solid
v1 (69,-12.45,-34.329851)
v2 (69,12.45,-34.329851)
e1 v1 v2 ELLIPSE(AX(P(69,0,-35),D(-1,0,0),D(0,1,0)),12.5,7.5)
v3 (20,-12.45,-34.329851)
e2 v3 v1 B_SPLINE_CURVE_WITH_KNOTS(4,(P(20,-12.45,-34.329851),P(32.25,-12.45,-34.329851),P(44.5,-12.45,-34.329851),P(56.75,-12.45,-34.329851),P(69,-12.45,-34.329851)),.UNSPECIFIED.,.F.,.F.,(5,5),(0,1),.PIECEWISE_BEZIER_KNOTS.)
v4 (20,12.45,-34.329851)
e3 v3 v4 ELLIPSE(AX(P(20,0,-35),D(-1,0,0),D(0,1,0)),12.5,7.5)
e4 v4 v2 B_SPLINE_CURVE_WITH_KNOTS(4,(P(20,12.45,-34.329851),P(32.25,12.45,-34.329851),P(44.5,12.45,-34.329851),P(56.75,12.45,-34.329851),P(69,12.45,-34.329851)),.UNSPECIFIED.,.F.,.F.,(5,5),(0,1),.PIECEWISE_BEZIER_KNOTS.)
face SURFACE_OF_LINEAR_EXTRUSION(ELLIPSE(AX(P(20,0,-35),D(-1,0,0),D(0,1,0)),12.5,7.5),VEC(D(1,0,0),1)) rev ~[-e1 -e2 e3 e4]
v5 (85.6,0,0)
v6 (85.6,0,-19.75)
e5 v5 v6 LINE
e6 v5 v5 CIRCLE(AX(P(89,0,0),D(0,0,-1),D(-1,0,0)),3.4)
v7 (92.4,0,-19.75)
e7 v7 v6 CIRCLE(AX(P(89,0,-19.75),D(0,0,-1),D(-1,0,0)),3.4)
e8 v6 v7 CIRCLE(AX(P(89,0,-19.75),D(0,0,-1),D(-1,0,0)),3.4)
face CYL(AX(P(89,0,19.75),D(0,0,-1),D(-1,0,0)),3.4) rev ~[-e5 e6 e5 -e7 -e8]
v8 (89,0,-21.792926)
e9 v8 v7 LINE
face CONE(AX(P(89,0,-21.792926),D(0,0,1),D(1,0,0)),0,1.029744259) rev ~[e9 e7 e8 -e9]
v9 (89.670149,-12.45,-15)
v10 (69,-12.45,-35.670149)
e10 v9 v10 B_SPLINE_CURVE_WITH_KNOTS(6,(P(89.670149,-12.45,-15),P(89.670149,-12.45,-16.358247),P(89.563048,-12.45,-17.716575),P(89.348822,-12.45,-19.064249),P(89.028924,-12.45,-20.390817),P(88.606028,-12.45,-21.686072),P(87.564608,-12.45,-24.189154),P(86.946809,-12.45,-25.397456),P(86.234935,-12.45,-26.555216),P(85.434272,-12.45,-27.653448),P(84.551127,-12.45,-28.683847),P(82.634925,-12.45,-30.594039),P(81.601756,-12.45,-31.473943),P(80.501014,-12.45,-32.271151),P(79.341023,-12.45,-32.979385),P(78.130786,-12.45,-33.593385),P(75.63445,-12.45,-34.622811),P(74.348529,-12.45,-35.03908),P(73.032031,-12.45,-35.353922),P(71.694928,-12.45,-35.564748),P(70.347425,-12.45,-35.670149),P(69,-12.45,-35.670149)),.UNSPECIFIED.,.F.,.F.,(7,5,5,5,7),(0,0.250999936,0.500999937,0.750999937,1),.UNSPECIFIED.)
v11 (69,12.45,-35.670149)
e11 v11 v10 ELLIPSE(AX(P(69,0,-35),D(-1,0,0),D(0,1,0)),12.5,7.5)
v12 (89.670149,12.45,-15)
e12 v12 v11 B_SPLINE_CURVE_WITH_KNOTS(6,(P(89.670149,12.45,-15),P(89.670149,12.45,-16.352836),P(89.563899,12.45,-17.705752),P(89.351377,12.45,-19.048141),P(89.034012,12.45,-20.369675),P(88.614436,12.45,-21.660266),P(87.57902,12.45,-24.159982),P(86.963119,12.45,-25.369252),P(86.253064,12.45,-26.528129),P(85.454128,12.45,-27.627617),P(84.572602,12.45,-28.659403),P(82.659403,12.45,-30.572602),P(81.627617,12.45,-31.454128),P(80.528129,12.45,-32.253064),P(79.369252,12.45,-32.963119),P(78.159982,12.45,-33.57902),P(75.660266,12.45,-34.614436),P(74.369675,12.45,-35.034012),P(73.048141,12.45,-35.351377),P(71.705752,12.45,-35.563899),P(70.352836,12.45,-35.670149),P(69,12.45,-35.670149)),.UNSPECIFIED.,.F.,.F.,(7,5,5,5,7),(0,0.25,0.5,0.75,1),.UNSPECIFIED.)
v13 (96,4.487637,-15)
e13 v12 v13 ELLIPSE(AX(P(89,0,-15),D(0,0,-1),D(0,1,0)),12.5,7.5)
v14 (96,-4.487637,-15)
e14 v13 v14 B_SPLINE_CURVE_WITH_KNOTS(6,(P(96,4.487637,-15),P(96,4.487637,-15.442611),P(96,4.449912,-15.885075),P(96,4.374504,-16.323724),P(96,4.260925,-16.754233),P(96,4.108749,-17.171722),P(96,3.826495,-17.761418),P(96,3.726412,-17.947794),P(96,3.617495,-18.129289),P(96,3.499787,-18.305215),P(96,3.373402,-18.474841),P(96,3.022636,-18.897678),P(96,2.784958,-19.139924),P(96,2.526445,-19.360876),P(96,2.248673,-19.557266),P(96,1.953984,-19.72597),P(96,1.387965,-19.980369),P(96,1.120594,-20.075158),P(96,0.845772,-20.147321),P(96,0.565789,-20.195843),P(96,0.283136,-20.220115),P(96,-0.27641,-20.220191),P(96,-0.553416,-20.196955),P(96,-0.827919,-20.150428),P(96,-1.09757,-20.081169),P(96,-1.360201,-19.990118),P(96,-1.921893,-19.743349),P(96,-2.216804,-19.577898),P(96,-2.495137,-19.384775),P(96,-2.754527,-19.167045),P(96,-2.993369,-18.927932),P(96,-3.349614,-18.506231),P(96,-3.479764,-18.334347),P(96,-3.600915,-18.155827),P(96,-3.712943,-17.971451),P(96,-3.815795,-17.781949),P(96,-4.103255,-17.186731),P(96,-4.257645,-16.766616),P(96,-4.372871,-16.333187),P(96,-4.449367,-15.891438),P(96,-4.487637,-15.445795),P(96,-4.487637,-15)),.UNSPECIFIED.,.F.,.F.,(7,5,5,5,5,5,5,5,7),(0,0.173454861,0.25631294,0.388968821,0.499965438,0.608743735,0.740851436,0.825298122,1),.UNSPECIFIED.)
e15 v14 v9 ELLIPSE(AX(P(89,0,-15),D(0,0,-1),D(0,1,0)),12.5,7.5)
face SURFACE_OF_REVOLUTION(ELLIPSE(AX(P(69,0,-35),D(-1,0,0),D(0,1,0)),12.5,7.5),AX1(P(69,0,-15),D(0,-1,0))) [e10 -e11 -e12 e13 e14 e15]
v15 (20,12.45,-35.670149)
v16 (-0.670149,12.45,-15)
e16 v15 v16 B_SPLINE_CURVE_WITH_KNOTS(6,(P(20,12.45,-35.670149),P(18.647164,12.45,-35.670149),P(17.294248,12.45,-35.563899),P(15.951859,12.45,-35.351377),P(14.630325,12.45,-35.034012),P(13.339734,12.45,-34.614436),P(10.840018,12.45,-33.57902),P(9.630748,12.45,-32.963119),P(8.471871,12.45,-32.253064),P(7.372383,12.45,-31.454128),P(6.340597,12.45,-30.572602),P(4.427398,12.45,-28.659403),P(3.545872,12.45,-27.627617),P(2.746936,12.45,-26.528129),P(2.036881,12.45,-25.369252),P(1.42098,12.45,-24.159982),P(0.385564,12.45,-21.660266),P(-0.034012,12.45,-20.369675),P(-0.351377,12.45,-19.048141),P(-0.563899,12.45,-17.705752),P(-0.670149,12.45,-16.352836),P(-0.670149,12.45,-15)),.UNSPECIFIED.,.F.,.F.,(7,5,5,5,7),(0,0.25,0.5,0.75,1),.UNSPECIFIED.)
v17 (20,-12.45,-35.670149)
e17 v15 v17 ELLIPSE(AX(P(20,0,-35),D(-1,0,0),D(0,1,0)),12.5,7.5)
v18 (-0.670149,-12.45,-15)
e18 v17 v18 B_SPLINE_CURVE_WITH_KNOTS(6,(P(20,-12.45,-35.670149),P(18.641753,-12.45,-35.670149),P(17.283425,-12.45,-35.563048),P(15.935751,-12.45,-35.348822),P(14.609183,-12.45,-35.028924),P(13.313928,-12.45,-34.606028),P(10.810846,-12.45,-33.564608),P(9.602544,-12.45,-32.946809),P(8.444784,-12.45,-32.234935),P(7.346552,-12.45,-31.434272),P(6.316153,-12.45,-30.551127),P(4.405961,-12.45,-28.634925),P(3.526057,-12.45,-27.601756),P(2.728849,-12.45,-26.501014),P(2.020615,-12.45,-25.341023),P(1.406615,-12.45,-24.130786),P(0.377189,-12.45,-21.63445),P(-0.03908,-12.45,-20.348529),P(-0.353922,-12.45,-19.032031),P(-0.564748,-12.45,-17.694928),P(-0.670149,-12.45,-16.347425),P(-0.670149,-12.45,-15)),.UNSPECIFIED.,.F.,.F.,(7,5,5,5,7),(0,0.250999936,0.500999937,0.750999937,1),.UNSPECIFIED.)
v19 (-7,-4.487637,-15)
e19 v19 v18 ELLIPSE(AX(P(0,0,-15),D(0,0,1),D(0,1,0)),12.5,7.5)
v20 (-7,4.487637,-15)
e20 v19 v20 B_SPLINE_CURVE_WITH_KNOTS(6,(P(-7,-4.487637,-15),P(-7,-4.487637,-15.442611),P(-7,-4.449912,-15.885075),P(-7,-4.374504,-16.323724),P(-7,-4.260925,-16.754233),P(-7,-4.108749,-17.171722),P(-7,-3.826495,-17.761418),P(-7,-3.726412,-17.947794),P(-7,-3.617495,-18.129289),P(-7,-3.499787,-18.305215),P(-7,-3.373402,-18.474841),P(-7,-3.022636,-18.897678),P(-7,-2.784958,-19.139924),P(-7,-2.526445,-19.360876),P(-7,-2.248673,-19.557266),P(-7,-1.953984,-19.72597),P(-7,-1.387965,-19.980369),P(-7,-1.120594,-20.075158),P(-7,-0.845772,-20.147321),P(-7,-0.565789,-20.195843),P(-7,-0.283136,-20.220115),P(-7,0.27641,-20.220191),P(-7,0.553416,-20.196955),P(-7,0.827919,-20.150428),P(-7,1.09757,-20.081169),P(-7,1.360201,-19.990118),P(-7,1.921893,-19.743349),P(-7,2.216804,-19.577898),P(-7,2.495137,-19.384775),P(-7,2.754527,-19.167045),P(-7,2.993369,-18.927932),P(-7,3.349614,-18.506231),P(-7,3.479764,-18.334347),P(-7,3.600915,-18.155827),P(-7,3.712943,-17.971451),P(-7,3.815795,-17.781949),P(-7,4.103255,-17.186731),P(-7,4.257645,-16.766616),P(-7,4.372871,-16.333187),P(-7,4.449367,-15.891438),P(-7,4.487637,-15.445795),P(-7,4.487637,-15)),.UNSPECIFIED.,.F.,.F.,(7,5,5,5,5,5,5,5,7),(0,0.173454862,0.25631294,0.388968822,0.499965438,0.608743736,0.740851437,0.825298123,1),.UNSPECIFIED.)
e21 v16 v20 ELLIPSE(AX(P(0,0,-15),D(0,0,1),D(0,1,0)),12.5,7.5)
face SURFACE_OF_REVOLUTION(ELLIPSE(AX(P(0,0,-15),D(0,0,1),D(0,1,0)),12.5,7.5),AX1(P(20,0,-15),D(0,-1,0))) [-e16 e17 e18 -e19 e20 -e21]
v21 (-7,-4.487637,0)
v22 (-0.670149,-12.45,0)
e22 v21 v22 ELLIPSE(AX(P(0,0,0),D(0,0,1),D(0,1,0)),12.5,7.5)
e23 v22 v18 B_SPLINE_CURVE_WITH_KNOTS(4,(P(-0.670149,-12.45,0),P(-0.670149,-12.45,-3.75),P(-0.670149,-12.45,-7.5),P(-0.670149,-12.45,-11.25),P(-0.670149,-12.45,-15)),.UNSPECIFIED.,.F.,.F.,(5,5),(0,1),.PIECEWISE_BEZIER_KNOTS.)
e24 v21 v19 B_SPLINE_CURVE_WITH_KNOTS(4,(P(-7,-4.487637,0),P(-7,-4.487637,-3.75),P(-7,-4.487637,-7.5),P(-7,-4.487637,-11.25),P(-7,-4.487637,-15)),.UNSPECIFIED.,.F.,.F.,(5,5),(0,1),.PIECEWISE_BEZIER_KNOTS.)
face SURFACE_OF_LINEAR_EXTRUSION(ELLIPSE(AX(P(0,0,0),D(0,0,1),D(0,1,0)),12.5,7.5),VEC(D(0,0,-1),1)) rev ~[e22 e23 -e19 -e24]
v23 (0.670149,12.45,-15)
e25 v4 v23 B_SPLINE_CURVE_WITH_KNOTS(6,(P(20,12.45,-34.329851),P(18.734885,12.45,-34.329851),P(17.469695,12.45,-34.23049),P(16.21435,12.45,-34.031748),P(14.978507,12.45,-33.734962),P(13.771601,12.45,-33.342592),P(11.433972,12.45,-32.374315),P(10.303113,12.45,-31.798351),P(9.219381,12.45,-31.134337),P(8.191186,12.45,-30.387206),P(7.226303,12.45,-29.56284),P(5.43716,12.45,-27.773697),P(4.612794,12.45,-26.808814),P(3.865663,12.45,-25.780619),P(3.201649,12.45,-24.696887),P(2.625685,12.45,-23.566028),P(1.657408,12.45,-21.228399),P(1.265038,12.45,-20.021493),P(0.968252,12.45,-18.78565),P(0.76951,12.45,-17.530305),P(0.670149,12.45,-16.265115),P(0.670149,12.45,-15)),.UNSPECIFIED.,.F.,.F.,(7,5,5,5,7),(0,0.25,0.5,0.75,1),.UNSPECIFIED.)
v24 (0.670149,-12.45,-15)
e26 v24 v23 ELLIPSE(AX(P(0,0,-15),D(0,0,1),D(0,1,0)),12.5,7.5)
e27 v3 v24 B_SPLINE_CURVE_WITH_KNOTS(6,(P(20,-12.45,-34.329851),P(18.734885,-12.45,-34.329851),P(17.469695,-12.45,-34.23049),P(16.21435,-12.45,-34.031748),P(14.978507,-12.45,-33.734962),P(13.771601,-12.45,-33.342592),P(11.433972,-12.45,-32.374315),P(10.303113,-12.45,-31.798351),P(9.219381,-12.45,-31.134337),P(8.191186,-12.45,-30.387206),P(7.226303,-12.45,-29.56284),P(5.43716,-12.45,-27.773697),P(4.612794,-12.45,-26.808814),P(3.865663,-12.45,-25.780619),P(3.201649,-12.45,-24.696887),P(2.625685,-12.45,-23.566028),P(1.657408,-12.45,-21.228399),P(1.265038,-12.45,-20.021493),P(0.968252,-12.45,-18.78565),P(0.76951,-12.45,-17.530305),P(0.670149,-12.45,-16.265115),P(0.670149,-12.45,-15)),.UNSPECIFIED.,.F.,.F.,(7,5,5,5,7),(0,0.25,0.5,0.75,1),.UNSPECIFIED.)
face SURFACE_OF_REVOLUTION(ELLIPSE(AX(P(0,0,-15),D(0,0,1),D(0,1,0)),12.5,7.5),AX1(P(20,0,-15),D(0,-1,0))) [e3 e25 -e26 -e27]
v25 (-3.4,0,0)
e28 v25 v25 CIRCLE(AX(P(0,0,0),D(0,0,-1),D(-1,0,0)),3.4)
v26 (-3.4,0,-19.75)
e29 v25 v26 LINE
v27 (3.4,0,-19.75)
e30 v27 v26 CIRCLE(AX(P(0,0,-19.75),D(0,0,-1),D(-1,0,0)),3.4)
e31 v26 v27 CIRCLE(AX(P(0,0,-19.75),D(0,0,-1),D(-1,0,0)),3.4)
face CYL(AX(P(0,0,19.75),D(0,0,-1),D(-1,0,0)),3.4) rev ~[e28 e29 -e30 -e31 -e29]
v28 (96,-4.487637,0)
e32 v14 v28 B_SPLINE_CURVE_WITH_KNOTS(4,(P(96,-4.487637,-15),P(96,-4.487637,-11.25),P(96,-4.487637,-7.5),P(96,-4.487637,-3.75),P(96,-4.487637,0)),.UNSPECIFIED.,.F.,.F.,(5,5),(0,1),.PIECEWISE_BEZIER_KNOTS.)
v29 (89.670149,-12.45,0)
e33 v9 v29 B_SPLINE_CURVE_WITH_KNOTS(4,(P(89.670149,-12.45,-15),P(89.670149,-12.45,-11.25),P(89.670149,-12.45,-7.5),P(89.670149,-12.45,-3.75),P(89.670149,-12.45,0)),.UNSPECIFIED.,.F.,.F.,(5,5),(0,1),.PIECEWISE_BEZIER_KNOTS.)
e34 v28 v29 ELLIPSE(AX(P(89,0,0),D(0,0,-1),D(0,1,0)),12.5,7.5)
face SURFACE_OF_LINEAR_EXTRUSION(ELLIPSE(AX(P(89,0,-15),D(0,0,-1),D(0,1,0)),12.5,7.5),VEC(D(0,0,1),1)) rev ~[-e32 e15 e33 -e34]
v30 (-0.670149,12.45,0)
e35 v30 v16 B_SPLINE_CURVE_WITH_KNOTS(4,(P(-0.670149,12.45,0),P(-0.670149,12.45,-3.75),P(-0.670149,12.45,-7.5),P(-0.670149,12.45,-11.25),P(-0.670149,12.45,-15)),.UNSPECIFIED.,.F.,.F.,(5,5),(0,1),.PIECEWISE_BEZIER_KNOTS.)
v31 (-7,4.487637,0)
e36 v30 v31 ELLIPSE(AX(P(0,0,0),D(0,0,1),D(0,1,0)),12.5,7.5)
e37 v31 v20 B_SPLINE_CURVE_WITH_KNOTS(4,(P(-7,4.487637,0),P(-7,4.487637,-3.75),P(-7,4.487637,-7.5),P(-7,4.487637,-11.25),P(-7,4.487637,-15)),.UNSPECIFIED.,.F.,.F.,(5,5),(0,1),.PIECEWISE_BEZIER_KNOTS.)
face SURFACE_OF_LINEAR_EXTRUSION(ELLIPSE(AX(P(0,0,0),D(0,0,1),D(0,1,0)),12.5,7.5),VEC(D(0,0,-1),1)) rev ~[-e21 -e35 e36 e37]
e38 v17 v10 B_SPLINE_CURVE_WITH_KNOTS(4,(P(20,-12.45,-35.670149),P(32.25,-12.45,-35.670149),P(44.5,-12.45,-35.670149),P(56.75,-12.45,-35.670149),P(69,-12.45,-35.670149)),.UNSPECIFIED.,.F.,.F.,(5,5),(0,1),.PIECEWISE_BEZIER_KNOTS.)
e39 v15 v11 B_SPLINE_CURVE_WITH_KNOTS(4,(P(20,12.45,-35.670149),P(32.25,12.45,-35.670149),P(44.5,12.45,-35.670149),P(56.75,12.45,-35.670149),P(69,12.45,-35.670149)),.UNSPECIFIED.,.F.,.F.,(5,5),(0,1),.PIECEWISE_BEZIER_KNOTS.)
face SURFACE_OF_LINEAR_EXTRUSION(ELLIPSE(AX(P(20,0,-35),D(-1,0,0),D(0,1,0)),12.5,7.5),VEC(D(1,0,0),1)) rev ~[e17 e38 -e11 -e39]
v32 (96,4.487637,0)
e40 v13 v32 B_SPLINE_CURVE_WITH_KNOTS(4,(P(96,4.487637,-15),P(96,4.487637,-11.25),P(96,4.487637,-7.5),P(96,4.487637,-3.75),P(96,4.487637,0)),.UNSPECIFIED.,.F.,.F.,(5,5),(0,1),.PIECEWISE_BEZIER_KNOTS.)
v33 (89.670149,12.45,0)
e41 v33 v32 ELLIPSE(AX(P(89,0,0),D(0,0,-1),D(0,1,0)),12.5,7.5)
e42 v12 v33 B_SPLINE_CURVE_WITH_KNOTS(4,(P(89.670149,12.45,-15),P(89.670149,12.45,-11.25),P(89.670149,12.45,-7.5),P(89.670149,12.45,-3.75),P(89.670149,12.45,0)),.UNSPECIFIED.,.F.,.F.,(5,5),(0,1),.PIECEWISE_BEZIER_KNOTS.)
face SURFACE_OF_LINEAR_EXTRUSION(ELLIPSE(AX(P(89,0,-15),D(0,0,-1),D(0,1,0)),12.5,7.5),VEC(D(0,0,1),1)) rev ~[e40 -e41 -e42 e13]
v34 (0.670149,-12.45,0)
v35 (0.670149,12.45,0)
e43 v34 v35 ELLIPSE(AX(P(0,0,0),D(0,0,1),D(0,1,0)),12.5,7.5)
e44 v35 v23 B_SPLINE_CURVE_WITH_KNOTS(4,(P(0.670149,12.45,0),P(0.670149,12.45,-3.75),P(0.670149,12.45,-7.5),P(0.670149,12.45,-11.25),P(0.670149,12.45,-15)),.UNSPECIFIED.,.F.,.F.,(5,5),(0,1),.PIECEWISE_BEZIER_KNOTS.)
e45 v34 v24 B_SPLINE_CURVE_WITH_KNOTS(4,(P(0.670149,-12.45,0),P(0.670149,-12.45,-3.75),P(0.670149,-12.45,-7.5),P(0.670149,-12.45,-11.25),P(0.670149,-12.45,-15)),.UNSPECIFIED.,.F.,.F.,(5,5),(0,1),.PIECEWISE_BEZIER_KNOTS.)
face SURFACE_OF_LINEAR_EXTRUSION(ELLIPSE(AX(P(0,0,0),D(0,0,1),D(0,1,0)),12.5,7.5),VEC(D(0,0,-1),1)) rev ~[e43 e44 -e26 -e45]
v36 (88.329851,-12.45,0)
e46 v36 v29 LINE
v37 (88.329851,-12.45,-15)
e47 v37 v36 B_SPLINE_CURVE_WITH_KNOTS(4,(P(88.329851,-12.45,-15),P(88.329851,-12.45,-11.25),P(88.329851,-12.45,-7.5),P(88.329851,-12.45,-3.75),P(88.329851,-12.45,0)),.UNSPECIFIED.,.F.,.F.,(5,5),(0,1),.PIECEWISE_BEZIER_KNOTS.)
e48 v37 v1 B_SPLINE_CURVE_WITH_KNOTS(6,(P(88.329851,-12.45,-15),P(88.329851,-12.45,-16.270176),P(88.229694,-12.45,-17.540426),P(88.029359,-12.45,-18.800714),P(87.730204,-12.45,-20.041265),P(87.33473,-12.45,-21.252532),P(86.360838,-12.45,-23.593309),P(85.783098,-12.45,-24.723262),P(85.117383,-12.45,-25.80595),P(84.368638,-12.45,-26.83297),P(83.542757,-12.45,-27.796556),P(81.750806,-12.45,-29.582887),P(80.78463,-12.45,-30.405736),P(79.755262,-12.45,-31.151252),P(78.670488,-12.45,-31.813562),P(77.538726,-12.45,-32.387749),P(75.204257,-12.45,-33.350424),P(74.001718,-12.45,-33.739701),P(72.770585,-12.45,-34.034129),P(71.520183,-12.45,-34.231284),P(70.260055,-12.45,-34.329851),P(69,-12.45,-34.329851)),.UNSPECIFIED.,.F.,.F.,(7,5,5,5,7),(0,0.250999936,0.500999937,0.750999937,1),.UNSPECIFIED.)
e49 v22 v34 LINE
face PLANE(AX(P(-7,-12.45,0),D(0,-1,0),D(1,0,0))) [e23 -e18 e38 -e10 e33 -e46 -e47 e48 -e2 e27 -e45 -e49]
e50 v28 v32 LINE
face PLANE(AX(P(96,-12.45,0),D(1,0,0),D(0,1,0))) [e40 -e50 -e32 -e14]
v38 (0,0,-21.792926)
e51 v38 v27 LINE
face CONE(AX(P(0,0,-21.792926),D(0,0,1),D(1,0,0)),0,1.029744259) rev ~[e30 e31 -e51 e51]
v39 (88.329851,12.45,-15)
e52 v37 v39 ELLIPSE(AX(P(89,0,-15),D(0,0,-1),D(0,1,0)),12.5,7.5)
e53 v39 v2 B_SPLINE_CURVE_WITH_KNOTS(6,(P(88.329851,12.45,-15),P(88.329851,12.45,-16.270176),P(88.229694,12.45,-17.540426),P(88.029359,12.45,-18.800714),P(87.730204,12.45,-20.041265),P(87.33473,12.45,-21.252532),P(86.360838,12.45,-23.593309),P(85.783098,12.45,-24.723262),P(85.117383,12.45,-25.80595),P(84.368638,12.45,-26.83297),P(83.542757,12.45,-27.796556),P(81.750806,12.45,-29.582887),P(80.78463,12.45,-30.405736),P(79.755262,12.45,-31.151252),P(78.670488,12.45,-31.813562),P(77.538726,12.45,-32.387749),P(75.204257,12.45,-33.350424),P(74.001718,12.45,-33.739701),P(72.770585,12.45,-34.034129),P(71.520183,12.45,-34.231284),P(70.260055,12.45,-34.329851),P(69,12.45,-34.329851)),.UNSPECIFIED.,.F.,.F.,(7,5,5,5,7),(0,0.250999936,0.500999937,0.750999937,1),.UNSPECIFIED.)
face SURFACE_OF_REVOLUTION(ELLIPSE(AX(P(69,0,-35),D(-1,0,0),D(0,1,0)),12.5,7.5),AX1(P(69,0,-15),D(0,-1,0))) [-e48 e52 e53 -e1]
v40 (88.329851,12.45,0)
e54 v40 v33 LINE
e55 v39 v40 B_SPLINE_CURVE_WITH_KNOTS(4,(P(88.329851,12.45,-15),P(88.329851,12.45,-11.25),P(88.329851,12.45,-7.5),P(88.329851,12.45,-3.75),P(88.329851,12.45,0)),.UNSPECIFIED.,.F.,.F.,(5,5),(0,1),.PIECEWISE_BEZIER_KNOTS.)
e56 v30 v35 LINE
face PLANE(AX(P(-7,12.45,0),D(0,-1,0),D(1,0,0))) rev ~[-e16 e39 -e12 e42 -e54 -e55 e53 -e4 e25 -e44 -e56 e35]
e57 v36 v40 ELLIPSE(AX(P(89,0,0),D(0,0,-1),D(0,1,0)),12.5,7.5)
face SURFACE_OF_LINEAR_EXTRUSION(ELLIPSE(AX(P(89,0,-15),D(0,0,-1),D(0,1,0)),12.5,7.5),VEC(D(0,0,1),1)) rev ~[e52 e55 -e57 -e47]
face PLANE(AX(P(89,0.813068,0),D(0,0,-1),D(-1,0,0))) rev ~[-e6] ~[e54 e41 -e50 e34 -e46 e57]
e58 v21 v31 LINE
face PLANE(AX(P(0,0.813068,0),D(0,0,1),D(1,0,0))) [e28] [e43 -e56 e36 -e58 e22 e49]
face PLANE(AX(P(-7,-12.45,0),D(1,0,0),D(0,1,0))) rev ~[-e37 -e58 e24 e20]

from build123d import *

# Parameters (mm, degrees)
SKETCH2_RX              = 12.5
SKETCH2_RY              = 7.5
M8_TAPPED_HOLE1_D       = 6.8
M8_TAPPED_HOLE1_DEPTH   = 19.75
M8_TAPPED_HOLE1_TIP     = 2.042926105
SKETCH6_W               = 123
SKETCH6_H               = 44.9
SKETCH6_W_2             = 103
SKETCH6_H_2             = 24.9
CUT_EXTRUDE_THIN1_DEPTH = 107.18262584


with BuildPart() as part:
    # Sweep1: sweep along a path in Sketch3
    with BuildLine(Plane(origin=(0, 0, 0), x_dir=(1, 0, 0), z_dir=(0, 1, 0))) as sweep1_path:
        Line((0, 0), (0, 15))
        ThreePointArc((0, 15), (5.857864376, 29.142135624), (20, 35))
        Line((20, 35), (69, 35))
        ThreePointArc((69, 35), (83.142135624, 29.142135624), (89, 15))
        Line((89, 15), (89, 0))
    # Sketch2 → Sweep1 (sweep)
    with BuildSketch(Plane.XY):
        with Locations(Location((0, 0), (0, 0, 90))):
            Ellipse(SKETCH2_RX, SKETCH2_RY)
    sweep(path=sweep1_path.line)

    # M8 Tapped Hole1
    with Locations(Plane.XY):
        with Locations((0, 0), (89, 0)):
            Hole(M8_TAPPED_HOLE1_D / 2, depth=M8_TAPPED_HOLE1_DEPTH)
            with Locations((0, 0, -(M8_TAPPED_HOLE1_DEPTH + M8_TAPPED_HOLE1_TIP / 2))):  # 118° drill point
                Cone(0, M8_TAPPED_HOLE1_D / 2, M8_TAPPED_HOLE1_TIP, mode=Mode.SUBTRACT)

    # Sketch6 → Cut-Extrude-Thin1 (cut, through all)
    with BuildSketch(Plane.XY):
        with Locations((44.5, 0)):
            Rectangle(SKETCH6_W, SKETCH6_H)
        with Locations((44.5, 0)):
            Rectangle(SKETCH6_W_2, SKETCH6_H_2, mode=Mode.SUBTRACT)
    extrude(amount=-CUT_EXTRUDE_THIN1_DEPTH, mode=Mode.SUBTRACT)


solid = part.part
